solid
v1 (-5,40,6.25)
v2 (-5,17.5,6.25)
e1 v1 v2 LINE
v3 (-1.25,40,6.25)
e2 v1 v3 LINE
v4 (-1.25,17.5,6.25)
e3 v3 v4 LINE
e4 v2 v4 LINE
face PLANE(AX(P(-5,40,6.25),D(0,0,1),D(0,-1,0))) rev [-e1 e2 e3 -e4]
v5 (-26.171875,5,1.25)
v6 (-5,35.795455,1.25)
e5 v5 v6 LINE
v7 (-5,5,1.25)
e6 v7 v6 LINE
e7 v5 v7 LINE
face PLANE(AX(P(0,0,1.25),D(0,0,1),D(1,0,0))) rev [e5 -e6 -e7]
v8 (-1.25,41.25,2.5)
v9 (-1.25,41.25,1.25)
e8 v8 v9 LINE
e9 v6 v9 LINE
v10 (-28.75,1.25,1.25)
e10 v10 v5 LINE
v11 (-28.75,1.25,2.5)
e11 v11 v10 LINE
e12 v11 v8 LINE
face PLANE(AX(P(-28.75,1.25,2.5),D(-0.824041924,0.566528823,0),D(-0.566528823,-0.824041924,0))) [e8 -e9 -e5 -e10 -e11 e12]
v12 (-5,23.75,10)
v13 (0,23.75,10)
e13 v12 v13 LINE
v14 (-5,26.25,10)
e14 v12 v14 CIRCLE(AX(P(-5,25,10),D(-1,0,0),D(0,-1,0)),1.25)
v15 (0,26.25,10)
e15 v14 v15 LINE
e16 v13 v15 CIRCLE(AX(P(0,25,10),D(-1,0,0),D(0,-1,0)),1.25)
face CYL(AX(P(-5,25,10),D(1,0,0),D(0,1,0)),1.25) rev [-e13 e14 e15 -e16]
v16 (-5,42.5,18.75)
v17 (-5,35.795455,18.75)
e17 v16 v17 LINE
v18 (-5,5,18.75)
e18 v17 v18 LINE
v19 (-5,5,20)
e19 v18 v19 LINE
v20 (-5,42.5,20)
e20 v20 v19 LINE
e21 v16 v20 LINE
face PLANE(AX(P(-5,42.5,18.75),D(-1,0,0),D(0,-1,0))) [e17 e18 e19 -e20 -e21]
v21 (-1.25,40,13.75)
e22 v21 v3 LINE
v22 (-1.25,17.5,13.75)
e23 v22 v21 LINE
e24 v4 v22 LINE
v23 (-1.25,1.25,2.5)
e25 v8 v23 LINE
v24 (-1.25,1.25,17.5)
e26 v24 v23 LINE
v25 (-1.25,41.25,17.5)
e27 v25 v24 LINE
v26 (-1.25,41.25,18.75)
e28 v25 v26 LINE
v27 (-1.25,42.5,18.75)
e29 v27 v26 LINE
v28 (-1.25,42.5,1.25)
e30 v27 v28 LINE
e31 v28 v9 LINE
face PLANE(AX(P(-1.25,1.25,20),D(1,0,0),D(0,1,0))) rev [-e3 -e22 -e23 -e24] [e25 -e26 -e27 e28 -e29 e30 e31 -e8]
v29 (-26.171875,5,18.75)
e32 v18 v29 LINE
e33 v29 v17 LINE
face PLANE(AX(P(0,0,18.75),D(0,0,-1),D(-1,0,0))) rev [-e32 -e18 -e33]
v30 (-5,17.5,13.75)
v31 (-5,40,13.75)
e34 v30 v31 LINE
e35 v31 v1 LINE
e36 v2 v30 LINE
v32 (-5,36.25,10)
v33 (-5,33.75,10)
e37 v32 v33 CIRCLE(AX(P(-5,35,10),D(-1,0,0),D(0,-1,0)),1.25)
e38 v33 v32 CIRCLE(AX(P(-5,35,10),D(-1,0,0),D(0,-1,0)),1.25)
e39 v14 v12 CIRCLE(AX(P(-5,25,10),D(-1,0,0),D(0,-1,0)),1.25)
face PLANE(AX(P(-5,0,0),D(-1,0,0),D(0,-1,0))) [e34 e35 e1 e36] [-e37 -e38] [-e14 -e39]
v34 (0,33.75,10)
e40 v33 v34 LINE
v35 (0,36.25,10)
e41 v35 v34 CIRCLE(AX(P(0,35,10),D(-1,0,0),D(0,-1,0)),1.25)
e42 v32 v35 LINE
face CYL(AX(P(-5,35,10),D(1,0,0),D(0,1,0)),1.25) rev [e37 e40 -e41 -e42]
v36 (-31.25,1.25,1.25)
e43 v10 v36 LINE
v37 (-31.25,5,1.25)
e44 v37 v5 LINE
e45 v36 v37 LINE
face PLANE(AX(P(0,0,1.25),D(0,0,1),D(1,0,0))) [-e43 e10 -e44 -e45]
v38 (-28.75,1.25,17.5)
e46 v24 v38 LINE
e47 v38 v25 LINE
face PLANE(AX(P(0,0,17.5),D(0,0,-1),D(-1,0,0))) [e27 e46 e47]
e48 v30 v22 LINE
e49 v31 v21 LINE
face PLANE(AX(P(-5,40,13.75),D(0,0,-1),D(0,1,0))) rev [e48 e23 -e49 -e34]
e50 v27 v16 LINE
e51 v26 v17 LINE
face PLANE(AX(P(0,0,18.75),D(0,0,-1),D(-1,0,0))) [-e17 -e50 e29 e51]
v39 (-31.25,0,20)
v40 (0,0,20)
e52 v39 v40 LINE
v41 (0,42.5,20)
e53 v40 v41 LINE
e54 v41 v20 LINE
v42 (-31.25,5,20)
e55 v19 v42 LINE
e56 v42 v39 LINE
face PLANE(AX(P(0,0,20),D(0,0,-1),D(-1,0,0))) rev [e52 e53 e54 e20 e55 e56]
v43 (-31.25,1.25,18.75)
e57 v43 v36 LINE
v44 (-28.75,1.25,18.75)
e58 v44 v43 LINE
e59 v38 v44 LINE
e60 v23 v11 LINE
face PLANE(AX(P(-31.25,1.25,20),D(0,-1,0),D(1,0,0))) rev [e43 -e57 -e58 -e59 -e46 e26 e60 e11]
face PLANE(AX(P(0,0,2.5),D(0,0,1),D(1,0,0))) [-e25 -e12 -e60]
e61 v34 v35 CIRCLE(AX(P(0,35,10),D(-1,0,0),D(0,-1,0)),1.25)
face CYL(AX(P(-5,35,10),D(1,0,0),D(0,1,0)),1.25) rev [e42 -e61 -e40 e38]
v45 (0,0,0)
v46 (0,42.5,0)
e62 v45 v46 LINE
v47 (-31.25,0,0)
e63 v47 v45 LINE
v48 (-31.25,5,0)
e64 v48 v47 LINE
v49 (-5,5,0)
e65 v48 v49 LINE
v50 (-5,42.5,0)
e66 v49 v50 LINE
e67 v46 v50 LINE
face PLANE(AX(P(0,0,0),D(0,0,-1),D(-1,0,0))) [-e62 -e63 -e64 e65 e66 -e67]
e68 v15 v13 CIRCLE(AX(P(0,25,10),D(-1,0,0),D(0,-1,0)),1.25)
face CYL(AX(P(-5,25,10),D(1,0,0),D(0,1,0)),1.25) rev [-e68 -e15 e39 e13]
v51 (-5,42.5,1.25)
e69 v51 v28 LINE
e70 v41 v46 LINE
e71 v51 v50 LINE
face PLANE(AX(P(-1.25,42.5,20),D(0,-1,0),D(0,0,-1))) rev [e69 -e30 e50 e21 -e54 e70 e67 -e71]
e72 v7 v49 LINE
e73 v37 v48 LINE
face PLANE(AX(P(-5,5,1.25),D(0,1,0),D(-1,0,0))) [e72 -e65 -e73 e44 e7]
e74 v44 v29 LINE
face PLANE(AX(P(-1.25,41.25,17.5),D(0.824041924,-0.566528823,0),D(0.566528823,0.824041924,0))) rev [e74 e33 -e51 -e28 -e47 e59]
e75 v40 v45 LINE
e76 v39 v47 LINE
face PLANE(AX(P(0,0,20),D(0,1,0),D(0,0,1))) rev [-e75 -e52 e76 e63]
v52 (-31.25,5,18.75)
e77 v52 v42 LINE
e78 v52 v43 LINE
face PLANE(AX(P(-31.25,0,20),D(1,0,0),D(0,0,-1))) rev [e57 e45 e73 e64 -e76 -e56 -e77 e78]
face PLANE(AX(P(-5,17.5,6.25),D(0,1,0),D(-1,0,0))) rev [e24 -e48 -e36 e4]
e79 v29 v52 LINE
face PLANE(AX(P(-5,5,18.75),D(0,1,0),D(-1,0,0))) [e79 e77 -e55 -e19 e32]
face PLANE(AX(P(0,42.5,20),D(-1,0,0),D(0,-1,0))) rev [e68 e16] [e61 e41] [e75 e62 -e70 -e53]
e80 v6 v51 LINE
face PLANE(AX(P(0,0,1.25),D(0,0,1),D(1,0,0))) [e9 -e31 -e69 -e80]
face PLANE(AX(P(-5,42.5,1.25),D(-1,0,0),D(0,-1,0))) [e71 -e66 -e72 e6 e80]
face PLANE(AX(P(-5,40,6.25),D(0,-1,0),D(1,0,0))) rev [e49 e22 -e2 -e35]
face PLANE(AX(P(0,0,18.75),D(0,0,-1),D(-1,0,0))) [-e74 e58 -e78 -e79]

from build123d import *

# Parameters (mm, degrees)
BRACKET_L_BODY_DEPTH    = 20
LIP_FLANGE_DEPTH        = 1.25
END_PLATE_DEPTH         = 1.25
GUSSET_A_28_75X40_DEPTH = 1.25
GUSSET_B_27_5X40_DEPTH  = 1.25
TAB_AND_HOLES_SKETCH_W  = 7.5
TAB_AND_HOLES_SKETCH_H  = 22.5
TAB_AND_HOLES_SKETCH_R  = 1.25
MOUNTING_TAB_DEPTH      = 3.75
MOUNTING_START          = -3.75
SKETCH8_2_R             = 1.25
MOUNTING_HOLES_DEPTH    = 3.75


with BuildPart() as part:
    # L-Profile Sketch → Bracket L-Body (new body)
    with BuildSketch(Plane.XY):
        Polygon((0, 42.5), (0, 0), (-31.25, 0), (-31.25, 1.25), (-1.25, 1.25), (-1.25, 42.5), align=None)
    extrude(amount=BRACKET_L_BODY_DEPTH)

    # Lip Flange Sketch → Lip Flange (add)
    with BuildSketch(Plane.XY.offset(20)):
        Polygon((-1.25, 42.5), (-5, 42.5), (-5, 5), (-31.25, 5), (-31.25, 1.25), (-1.25, 1.25), align=None)
    extrude(amount=-LIP_FLANGE_DEPTH)

    # End Plate Sketch → End Plate (add)
    with BuildSketch(Plane(origin=(0, 0, 0), x_dir=(-1, 0, 0), z_dir=(0, 0, -1))):
        Polygon((0, 42.5), (1.25, 42.5), (5, 42.5), (5, 5), (31.25, 5), (31.25, 1.25), (31.25, 0), (0, 0), align=None)
    extrude(amount=-END_PLATE_DEPTH)

    # Gusset A Sketch → Gusset A 28.75x40 (add)
    with BuildSketch(Plane.XY.offset(1.25)):
        Polygon((-28.75, 1.25), (-1.25, 41.25), (-1.25, 1.25), align=None)
    extrude(amount=GUSSET_A_28_75X40_DEPTH)

    # Gusset B Sketch → Gusset B 27.5x40 (add)
    with BuildSketch(Plane(origin=(0, 0, 18.75), x_dir=(-1, 0, 0), z_dir=(0, 0, -1))):
        Polygon((1.25, 41.25), (28.75, 1.25), (1.25, 1.25), align=None)
    extrude(amount=GUSSET_B_27_5X40_DEPTH)

    # Tab And Holes Sketch → Mounting Tab (add)
    with BuildSketch(Plane.ZY.offset(1.25)):
        with Locations((10, 28.75)):
            Rectangle(TAB_AND_HOLES_SKETCH_W, TAB_AND_HOLES_SKETCH_H)
        with Locations(Location((10, 35, 0), (0, 0, 270))):
            Circle(TAB_AND_HOLES_SKETCH_R, mode=Mode.SUBTRACT)
        with Locations(Location((10, 25, 0), (0, 0, 270))):
            Circle(TAB_AND_HOLES_SKETCH_R, mode=Mode.SUBTRACT)
    extrude(amount=MOUNTING_TAB_DEPTH)

    # Sketch8_2 → Mounting Holes (cut)
    with BuildSketch(Plane.ZY.offset(1.25).offset(MOUNTING_START)):
        with Locations(Location((10, 35, 0), (0, 0, 270))):
            Circle(SKETCH8_2_R)
        with Locations(Location((10, 25, 0), (0, 0, 270))):
            Circle(SKETCH8_2_R)
    extrude(amount=MOUNTING_HOLES_DEPTH, mode=Mode.SUBTRACT)


solid = part.part
